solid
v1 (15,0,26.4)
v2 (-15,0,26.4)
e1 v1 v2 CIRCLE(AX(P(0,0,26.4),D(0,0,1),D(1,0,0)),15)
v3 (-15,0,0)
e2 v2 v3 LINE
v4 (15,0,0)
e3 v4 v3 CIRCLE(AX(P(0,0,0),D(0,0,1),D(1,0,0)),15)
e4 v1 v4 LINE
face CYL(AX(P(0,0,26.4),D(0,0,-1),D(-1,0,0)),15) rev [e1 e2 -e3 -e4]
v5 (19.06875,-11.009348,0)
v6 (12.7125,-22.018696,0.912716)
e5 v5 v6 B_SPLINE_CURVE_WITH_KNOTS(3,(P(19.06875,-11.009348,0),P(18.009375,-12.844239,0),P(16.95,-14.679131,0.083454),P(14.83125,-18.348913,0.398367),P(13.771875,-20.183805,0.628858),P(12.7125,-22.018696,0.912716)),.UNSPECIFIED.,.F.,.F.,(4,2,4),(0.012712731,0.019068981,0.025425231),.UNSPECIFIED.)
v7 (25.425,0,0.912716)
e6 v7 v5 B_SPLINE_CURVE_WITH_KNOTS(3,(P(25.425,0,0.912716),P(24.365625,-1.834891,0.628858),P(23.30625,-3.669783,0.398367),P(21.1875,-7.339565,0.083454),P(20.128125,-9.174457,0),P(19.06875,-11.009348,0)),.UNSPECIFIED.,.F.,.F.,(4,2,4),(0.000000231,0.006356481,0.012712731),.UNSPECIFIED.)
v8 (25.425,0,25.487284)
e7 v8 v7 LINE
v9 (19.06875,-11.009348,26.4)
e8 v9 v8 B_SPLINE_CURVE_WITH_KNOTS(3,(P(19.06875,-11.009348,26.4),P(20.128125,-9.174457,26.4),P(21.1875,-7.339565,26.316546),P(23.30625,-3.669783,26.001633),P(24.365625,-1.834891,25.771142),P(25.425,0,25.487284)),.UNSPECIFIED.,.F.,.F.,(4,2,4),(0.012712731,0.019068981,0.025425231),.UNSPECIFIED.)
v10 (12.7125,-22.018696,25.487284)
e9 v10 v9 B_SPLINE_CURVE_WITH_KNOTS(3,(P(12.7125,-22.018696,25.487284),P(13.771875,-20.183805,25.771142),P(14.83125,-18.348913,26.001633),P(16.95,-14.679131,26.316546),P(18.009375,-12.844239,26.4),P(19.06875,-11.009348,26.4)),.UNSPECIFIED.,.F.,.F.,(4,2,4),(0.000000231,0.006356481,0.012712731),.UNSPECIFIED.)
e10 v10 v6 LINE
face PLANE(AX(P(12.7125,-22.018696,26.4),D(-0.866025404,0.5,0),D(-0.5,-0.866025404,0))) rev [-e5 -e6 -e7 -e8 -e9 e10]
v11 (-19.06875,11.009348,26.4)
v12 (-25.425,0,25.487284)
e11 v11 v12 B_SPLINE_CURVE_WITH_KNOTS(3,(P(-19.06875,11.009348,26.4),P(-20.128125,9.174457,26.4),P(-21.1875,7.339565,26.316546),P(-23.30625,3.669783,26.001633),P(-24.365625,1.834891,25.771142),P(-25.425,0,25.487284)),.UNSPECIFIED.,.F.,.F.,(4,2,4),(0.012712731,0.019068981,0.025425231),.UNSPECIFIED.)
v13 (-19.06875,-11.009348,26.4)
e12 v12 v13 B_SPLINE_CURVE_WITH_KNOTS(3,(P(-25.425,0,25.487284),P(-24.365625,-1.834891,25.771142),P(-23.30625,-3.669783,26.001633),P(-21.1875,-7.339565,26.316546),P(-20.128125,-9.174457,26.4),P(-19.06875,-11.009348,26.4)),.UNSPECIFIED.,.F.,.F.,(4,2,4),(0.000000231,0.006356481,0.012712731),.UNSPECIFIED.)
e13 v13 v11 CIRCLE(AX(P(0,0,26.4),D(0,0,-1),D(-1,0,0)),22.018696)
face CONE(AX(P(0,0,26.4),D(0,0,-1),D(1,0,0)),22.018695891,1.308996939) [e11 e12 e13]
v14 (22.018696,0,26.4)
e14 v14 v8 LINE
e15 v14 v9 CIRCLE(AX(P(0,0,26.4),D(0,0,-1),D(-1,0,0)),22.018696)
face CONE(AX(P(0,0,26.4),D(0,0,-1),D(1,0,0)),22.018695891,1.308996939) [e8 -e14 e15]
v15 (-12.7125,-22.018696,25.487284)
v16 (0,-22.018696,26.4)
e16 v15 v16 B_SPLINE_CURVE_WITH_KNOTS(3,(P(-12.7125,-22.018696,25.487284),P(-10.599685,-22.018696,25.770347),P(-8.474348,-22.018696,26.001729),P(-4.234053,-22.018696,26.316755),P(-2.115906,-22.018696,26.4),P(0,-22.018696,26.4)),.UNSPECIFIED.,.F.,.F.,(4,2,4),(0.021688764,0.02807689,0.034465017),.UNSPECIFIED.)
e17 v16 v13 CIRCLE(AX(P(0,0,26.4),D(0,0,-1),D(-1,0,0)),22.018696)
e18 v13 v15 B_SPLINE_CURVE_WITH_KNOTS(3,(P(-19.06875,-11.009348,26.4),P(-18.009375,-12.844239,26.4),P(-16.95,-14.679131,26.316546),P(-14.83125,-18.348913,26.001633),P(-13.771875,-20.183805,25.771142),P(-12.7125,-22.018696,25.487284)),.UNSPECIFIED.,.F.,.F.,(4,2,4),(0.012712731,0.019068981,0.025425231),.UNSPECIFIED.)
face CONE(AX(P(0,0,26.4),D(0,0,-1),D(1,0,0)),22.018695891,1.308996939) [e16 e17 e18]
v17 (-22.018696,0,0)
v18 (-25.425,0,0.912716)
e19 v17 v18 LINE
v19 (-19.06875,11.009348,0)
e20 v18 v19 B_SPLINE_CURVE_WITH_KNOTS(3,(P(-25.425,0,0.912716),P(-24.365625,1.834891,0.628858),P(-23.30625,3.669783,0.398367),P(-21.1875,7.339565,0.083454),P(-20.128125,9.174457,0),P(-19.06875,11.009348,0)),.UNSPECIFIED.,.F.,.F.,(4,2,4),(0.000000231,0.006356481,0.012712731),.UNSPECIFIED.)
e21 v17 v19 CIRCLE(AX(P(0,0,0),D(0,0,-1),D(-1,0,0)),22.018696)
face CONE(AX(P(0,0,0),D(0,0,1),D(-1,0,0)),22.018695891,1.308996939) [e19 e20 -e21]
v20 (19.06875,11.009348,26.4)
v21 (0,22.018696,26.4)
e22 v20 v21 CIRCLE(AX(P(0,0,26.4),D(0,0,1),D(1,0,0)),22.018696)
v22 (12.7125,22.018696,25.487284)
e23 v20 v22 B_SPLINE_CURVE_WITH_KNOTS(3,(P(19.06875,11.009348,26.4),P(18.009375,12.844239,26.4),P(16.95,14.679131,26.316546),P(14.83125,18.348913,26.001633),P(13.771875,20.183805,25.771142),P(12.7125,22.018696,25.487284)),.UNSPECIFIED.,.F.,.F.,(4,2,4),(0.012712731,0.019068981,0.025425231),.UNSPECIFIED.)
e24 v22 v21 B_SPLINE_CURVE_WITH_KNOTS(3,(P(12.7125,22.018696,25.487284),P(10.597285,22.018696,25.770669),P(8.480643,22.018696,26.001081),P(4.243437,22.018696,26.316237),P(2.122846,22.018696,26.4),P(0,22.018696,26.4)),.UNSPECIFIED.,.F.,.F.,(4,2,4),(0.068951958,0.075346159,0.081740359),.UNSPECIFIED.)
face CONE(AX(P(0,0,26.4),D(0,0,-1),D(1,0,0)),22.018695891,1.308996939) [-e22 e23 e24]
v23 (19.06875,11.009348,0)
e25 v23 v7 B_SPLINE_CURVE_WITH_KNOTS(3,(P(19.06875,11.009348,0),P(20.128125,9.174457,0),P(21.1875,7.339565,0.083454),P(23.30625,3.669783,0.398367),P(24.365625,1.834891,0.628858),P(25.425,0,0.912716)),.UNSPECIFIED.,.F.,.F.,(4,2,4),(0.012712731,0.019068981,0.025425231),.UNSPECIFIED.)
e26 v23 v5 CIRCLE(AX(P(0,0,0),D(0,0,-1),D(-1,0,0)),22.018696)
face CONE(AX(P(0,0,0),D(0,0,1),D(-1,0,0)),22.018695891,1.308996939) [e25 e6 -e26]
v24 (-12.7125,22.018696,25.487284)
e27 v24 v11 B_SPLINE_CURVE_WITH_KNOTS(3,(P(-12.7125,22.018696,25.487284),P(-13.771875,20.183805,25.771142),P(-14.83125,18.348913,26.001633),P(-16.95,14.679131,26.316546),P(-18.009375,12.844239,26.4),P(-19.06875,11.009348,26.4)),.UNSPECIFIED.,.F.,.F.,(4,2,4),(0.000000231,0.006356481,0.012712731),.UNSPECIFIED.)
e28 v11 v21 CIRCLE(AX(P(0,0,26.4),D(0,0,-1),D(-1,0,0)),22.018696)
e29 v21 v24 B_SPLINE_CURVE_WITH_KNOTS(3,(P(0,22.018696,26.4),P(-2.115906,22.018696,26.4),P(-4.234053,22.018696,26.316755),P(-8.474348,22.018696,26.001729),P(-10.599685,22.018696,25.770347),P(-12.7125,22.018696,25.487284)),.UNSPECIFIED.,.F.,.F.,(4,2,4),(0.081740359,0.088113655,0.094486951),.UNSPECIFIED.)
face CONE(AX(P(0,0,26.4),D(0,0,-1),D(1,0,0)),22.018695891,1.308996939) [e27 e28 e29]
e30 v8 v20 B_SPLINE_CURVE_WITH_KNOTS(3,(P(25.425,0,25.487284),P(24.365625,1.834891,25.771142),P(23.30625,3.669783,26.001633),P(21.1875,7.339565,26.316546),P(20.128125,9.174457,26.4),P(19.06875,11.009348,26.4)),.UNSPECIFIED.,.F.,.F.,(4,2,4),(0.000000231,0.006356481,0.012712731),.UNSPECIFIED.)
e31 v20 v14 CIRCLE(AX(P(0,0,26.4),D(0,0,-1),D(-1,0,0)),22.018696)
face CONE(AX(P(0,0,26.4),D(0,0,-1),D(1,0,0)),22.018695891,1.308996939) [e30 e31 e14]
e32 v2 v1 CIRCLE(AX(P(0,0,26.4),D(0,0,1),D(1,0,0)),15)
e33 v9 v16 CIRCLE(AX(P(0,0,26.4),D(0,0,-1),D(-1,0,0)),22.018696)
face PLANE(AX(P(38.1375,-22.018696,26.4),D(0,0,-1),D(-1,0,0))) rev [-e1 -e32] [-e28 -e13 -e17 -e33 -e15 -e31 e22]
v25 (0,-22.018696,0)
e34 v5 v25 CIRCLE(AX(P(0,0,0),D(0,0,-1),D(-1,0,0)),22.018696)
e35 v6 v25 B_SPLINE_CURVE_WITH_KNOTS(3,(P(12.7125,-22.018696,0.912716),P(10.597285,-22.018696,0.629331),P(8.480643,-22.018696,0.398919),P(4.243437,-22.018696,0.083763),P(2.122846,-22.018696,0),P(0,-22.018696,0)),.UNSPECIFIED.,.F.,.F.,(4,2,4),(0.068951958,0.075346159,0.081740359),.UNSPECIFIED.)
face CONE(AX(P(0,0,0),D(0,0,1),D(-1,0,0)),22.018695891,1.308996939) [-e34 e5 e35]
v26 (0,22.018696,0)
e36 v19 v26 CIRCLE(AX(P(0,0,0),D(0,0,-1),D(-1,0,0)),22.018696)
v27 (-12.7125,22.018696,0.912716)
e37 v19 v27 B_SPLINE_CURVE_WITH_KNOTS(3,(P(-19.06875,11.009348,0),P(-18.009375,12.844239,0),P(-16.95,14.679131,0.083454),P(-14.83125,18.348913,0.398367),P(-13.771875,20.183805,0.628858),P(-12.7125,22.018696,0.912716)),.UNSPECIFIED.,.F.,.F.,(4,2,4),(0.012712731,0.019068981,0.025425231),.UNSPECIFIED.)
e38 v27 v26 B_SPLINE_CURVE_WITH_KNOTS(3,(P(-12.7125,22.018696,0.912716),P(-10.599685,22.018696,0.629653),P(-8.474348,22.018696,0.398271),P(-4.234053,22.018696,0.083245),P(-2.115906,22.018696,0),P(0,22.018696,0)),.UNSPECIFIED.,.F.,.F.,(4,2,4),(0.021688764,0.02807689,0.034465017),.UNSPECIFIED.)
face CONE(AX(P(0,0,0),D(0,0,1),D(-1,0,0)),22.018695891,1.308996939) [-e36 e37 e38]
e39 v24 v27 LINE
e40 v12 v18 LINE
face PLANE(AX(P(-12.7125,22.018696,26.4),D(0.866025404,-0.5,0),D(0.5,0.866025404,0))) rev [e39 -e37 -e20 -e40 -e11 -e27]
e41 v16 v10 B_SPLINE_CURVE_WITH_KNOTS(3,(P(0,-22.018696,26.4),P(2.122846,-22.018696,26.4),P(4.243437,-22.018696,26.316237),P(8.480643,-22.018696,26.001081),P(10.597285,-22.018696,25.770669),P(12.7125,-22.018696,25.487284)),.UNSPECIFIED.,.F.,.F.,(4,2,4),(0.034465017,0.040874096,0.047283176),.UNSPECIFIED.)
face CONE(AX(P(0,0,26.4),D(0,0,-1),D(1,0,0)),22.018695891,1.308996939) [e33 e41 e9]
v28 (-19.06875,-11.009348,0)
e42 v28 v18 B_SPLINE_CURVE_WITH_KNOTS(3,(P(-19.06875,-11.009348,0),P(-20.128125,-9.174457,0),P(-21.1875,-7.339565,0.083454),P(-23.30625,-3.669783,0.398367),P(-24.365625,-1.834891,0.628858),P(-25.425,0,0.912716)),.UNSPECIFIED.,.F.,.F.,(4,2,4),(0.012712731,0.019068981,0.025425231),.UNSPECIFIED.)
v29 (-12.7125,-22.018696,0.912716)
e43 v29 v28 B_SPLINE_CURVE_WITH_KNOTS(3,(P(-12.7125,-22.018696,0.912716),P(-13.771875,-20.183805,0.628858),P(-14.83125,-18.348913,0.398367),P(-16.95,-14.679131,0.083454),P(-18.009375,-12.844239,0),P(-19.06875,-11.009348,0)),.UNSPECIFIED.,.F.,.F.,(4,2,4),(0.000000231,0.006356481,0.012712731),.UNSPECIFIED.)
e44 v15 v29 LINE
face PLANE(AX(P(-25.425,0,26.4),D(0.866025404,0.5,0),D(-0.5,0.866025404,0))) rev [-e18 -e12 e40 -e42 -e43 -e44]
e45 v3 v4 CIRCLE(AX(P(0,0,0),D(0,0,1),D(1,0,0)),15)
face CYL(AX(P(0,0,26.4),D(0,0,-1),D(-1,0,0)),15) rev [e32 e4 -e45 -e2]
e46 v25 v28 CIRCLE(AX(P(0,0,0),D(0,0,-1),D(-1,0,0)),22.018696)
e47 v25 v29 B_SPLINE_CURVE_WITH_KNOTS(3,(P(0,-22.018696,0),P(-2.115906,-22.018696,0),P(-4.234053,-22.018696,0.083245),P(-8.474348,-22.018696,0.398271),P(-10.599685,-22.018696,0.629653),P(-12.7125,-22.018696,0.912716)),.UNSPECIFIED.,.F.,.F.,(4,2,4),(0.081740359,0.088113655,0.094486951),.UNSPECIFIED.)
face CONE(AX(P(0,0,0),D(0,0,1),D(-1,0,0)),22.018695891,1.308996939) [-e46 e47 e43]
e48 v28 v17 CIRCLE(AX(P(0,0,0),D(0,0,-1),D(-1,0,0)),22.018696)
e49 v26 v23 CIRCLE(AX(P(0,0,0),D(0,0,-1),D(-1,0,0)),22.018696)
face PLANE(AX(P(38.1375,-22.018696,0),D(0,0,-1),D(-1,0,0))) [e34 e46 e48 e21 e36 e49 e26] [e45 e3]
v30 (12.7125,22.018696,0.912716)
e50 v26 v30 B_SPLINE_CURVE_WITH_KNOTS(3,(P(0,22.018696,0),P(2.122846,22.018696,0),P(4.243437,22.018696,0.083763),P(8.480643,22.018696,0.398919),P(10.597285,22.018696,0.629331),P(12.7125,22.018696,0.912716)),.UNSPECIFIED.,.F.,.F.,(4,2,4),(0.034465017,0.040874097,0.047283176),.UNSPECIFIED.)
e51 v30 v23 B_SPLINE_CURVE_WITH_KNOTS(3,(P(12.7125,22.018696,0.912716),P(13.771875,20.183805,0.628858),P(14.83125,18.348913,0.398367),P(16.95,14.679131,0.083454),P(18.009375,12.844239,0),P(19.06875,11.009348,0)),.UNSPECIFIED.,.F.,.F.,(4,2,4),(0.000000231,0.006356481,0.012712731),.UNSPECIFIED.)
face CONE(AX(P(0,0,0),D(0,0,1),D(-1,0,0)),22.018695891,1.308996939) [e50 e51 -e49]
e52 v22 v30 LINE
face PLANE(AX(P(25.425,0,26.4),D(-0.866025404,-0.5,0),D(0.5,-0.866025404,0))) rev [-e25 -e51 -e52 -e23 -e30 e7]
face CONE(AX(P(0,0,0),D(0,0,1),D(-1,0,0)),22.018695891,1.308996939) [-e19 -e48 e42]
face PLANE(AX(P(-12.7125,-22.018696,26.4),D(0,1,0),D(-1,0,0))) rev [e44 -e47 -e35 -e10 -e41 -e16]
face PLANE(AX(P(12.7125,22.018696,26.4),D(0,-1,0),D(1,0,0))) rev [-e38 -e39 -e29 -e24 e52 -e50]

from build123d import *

# Parameters (mm, degrees)
SKETCH1_R          = 15
BASE_EXTRUDE_DEPTH = 26.4
SKETCH2_OUTSIDE_W  = 350.938
SKETCH2_OUTSIDE_H  = 344.126
SKETCH2_OUTSIDE_R  = 22.018695891
CUT_EXTRUDE1_DEPTH = 38
CUT_EXTRUDE1_DRAFT = -75
SKETCH3_OUTSIDE_W  = 350.938
SKETCH3_OUTSIDE_H  = 344.126
SKETCH3_OUTSIDE_R  = 22.018695891
CUT_EXTRUDE2_DEPTH = 38
CUT_EXTRUDE2_DRAFT = -75


with BuildPart() as part:
    # Sketch1 → Base-Extrude (new body)
    with BuildSketch(Plane.XY):
        Polygon((12.7125, 22.018695891), (-12.7125, 22.018695891), (-25.425, 0), (-12.7125, -22.018695891), (12.7125, -22.018695891), (25.425, 0), align=None)
        Circle(SKETCH1_R, mode=Mode.SUBTRACT)
    extrude(amount=BASE_EXTRUDE_DEPTH)


with BuildPart() as cut_extrude1_tool:
    # Sketch2 outside → Cut-Extrude1 (with draft: the straight prism first)
    with BuildSketch(Plane(origin=(0, 0, 0), x_dir=(-1, 0, 0), z_dir=(0, 0, -1))):
        Rectangle(SKETCH2_OUTSIDE_W, SKETCH2_OUTSIDE_H)
        Circle(SKETCH2_OUTSIDE_R, mode=Mode.SUBTRACT)
    extrude(amount=-CUT_EXTRUDE1_DEPTH)
    # Cut-Extrude1: the draft: its side faces are tilted about the plane it starts from
    cut_extrude1_sides = [cut_extrude1_tool.faces().sort_by_distance(p)[0] for p in [
        (0, -172.063, 19),
        (-175.469, 0, 19),
        (0, 172.063, 19),
        (175.469, 0, 19),
        (22.018695891, 0, 19),
    ]]
    draft(cut_extrude1_sides, Plane(origin=(0, 0, 0), x_dir=(-1, 0, 0), z_dir=(0, 0, -1)), CUT_EXTRUDE1_DRAFT)


with BuildPart() as part_1:
    add(part.part)

    # Cut-Extrude1: cut by cut_extrude1_tool
    add(cut_extrude1_tool.part, mode=Mode.SUBTRACT)


with BuildPart() as cut_extrude2_tool:
    # Sketch3 outside → Cut-Extrude2 (with draft: the straight prism first)
    with BuildSketch(Plane.XY.offset(26.4)):
        Rectangle(SKETCH3_OUTSIDE_W, SKETCH3_OUTSIDE_H)
        Circle(SKETCH3_OUTSIDE_R, mode=Mode.SUBTRACT)
    extrude(amount=-CUT_EXTRUDE2_DEPTH)
    # Cut-Extrude2: the draft: its side faces are tilted about the plane it starts from
    cut_extrude2_sides = [cut_extrude2_tool.faces().sort_by_distance(p)[0] for p in [
        (0, -172.063, 7.4),
        (175.469, 0, 7.4),
        (0, 172.063, 7.4),
        (-175.469, 0, 7.4),
        (-22.018695891, 0, 7.4),
    ]]
    draft(cut_extrude2_sides, Plane.XY.offset(26.4), CUT_EXTRUDE2_DRAFT)


with BuildPart() as part_2:
    add(part_1.part)

    # Cut-Extrude2: cut by cut_extrude2_tool
    add(cut_extrude2_tool.part, mode=Mode.SUBTRACT)


solid = part_2.part
